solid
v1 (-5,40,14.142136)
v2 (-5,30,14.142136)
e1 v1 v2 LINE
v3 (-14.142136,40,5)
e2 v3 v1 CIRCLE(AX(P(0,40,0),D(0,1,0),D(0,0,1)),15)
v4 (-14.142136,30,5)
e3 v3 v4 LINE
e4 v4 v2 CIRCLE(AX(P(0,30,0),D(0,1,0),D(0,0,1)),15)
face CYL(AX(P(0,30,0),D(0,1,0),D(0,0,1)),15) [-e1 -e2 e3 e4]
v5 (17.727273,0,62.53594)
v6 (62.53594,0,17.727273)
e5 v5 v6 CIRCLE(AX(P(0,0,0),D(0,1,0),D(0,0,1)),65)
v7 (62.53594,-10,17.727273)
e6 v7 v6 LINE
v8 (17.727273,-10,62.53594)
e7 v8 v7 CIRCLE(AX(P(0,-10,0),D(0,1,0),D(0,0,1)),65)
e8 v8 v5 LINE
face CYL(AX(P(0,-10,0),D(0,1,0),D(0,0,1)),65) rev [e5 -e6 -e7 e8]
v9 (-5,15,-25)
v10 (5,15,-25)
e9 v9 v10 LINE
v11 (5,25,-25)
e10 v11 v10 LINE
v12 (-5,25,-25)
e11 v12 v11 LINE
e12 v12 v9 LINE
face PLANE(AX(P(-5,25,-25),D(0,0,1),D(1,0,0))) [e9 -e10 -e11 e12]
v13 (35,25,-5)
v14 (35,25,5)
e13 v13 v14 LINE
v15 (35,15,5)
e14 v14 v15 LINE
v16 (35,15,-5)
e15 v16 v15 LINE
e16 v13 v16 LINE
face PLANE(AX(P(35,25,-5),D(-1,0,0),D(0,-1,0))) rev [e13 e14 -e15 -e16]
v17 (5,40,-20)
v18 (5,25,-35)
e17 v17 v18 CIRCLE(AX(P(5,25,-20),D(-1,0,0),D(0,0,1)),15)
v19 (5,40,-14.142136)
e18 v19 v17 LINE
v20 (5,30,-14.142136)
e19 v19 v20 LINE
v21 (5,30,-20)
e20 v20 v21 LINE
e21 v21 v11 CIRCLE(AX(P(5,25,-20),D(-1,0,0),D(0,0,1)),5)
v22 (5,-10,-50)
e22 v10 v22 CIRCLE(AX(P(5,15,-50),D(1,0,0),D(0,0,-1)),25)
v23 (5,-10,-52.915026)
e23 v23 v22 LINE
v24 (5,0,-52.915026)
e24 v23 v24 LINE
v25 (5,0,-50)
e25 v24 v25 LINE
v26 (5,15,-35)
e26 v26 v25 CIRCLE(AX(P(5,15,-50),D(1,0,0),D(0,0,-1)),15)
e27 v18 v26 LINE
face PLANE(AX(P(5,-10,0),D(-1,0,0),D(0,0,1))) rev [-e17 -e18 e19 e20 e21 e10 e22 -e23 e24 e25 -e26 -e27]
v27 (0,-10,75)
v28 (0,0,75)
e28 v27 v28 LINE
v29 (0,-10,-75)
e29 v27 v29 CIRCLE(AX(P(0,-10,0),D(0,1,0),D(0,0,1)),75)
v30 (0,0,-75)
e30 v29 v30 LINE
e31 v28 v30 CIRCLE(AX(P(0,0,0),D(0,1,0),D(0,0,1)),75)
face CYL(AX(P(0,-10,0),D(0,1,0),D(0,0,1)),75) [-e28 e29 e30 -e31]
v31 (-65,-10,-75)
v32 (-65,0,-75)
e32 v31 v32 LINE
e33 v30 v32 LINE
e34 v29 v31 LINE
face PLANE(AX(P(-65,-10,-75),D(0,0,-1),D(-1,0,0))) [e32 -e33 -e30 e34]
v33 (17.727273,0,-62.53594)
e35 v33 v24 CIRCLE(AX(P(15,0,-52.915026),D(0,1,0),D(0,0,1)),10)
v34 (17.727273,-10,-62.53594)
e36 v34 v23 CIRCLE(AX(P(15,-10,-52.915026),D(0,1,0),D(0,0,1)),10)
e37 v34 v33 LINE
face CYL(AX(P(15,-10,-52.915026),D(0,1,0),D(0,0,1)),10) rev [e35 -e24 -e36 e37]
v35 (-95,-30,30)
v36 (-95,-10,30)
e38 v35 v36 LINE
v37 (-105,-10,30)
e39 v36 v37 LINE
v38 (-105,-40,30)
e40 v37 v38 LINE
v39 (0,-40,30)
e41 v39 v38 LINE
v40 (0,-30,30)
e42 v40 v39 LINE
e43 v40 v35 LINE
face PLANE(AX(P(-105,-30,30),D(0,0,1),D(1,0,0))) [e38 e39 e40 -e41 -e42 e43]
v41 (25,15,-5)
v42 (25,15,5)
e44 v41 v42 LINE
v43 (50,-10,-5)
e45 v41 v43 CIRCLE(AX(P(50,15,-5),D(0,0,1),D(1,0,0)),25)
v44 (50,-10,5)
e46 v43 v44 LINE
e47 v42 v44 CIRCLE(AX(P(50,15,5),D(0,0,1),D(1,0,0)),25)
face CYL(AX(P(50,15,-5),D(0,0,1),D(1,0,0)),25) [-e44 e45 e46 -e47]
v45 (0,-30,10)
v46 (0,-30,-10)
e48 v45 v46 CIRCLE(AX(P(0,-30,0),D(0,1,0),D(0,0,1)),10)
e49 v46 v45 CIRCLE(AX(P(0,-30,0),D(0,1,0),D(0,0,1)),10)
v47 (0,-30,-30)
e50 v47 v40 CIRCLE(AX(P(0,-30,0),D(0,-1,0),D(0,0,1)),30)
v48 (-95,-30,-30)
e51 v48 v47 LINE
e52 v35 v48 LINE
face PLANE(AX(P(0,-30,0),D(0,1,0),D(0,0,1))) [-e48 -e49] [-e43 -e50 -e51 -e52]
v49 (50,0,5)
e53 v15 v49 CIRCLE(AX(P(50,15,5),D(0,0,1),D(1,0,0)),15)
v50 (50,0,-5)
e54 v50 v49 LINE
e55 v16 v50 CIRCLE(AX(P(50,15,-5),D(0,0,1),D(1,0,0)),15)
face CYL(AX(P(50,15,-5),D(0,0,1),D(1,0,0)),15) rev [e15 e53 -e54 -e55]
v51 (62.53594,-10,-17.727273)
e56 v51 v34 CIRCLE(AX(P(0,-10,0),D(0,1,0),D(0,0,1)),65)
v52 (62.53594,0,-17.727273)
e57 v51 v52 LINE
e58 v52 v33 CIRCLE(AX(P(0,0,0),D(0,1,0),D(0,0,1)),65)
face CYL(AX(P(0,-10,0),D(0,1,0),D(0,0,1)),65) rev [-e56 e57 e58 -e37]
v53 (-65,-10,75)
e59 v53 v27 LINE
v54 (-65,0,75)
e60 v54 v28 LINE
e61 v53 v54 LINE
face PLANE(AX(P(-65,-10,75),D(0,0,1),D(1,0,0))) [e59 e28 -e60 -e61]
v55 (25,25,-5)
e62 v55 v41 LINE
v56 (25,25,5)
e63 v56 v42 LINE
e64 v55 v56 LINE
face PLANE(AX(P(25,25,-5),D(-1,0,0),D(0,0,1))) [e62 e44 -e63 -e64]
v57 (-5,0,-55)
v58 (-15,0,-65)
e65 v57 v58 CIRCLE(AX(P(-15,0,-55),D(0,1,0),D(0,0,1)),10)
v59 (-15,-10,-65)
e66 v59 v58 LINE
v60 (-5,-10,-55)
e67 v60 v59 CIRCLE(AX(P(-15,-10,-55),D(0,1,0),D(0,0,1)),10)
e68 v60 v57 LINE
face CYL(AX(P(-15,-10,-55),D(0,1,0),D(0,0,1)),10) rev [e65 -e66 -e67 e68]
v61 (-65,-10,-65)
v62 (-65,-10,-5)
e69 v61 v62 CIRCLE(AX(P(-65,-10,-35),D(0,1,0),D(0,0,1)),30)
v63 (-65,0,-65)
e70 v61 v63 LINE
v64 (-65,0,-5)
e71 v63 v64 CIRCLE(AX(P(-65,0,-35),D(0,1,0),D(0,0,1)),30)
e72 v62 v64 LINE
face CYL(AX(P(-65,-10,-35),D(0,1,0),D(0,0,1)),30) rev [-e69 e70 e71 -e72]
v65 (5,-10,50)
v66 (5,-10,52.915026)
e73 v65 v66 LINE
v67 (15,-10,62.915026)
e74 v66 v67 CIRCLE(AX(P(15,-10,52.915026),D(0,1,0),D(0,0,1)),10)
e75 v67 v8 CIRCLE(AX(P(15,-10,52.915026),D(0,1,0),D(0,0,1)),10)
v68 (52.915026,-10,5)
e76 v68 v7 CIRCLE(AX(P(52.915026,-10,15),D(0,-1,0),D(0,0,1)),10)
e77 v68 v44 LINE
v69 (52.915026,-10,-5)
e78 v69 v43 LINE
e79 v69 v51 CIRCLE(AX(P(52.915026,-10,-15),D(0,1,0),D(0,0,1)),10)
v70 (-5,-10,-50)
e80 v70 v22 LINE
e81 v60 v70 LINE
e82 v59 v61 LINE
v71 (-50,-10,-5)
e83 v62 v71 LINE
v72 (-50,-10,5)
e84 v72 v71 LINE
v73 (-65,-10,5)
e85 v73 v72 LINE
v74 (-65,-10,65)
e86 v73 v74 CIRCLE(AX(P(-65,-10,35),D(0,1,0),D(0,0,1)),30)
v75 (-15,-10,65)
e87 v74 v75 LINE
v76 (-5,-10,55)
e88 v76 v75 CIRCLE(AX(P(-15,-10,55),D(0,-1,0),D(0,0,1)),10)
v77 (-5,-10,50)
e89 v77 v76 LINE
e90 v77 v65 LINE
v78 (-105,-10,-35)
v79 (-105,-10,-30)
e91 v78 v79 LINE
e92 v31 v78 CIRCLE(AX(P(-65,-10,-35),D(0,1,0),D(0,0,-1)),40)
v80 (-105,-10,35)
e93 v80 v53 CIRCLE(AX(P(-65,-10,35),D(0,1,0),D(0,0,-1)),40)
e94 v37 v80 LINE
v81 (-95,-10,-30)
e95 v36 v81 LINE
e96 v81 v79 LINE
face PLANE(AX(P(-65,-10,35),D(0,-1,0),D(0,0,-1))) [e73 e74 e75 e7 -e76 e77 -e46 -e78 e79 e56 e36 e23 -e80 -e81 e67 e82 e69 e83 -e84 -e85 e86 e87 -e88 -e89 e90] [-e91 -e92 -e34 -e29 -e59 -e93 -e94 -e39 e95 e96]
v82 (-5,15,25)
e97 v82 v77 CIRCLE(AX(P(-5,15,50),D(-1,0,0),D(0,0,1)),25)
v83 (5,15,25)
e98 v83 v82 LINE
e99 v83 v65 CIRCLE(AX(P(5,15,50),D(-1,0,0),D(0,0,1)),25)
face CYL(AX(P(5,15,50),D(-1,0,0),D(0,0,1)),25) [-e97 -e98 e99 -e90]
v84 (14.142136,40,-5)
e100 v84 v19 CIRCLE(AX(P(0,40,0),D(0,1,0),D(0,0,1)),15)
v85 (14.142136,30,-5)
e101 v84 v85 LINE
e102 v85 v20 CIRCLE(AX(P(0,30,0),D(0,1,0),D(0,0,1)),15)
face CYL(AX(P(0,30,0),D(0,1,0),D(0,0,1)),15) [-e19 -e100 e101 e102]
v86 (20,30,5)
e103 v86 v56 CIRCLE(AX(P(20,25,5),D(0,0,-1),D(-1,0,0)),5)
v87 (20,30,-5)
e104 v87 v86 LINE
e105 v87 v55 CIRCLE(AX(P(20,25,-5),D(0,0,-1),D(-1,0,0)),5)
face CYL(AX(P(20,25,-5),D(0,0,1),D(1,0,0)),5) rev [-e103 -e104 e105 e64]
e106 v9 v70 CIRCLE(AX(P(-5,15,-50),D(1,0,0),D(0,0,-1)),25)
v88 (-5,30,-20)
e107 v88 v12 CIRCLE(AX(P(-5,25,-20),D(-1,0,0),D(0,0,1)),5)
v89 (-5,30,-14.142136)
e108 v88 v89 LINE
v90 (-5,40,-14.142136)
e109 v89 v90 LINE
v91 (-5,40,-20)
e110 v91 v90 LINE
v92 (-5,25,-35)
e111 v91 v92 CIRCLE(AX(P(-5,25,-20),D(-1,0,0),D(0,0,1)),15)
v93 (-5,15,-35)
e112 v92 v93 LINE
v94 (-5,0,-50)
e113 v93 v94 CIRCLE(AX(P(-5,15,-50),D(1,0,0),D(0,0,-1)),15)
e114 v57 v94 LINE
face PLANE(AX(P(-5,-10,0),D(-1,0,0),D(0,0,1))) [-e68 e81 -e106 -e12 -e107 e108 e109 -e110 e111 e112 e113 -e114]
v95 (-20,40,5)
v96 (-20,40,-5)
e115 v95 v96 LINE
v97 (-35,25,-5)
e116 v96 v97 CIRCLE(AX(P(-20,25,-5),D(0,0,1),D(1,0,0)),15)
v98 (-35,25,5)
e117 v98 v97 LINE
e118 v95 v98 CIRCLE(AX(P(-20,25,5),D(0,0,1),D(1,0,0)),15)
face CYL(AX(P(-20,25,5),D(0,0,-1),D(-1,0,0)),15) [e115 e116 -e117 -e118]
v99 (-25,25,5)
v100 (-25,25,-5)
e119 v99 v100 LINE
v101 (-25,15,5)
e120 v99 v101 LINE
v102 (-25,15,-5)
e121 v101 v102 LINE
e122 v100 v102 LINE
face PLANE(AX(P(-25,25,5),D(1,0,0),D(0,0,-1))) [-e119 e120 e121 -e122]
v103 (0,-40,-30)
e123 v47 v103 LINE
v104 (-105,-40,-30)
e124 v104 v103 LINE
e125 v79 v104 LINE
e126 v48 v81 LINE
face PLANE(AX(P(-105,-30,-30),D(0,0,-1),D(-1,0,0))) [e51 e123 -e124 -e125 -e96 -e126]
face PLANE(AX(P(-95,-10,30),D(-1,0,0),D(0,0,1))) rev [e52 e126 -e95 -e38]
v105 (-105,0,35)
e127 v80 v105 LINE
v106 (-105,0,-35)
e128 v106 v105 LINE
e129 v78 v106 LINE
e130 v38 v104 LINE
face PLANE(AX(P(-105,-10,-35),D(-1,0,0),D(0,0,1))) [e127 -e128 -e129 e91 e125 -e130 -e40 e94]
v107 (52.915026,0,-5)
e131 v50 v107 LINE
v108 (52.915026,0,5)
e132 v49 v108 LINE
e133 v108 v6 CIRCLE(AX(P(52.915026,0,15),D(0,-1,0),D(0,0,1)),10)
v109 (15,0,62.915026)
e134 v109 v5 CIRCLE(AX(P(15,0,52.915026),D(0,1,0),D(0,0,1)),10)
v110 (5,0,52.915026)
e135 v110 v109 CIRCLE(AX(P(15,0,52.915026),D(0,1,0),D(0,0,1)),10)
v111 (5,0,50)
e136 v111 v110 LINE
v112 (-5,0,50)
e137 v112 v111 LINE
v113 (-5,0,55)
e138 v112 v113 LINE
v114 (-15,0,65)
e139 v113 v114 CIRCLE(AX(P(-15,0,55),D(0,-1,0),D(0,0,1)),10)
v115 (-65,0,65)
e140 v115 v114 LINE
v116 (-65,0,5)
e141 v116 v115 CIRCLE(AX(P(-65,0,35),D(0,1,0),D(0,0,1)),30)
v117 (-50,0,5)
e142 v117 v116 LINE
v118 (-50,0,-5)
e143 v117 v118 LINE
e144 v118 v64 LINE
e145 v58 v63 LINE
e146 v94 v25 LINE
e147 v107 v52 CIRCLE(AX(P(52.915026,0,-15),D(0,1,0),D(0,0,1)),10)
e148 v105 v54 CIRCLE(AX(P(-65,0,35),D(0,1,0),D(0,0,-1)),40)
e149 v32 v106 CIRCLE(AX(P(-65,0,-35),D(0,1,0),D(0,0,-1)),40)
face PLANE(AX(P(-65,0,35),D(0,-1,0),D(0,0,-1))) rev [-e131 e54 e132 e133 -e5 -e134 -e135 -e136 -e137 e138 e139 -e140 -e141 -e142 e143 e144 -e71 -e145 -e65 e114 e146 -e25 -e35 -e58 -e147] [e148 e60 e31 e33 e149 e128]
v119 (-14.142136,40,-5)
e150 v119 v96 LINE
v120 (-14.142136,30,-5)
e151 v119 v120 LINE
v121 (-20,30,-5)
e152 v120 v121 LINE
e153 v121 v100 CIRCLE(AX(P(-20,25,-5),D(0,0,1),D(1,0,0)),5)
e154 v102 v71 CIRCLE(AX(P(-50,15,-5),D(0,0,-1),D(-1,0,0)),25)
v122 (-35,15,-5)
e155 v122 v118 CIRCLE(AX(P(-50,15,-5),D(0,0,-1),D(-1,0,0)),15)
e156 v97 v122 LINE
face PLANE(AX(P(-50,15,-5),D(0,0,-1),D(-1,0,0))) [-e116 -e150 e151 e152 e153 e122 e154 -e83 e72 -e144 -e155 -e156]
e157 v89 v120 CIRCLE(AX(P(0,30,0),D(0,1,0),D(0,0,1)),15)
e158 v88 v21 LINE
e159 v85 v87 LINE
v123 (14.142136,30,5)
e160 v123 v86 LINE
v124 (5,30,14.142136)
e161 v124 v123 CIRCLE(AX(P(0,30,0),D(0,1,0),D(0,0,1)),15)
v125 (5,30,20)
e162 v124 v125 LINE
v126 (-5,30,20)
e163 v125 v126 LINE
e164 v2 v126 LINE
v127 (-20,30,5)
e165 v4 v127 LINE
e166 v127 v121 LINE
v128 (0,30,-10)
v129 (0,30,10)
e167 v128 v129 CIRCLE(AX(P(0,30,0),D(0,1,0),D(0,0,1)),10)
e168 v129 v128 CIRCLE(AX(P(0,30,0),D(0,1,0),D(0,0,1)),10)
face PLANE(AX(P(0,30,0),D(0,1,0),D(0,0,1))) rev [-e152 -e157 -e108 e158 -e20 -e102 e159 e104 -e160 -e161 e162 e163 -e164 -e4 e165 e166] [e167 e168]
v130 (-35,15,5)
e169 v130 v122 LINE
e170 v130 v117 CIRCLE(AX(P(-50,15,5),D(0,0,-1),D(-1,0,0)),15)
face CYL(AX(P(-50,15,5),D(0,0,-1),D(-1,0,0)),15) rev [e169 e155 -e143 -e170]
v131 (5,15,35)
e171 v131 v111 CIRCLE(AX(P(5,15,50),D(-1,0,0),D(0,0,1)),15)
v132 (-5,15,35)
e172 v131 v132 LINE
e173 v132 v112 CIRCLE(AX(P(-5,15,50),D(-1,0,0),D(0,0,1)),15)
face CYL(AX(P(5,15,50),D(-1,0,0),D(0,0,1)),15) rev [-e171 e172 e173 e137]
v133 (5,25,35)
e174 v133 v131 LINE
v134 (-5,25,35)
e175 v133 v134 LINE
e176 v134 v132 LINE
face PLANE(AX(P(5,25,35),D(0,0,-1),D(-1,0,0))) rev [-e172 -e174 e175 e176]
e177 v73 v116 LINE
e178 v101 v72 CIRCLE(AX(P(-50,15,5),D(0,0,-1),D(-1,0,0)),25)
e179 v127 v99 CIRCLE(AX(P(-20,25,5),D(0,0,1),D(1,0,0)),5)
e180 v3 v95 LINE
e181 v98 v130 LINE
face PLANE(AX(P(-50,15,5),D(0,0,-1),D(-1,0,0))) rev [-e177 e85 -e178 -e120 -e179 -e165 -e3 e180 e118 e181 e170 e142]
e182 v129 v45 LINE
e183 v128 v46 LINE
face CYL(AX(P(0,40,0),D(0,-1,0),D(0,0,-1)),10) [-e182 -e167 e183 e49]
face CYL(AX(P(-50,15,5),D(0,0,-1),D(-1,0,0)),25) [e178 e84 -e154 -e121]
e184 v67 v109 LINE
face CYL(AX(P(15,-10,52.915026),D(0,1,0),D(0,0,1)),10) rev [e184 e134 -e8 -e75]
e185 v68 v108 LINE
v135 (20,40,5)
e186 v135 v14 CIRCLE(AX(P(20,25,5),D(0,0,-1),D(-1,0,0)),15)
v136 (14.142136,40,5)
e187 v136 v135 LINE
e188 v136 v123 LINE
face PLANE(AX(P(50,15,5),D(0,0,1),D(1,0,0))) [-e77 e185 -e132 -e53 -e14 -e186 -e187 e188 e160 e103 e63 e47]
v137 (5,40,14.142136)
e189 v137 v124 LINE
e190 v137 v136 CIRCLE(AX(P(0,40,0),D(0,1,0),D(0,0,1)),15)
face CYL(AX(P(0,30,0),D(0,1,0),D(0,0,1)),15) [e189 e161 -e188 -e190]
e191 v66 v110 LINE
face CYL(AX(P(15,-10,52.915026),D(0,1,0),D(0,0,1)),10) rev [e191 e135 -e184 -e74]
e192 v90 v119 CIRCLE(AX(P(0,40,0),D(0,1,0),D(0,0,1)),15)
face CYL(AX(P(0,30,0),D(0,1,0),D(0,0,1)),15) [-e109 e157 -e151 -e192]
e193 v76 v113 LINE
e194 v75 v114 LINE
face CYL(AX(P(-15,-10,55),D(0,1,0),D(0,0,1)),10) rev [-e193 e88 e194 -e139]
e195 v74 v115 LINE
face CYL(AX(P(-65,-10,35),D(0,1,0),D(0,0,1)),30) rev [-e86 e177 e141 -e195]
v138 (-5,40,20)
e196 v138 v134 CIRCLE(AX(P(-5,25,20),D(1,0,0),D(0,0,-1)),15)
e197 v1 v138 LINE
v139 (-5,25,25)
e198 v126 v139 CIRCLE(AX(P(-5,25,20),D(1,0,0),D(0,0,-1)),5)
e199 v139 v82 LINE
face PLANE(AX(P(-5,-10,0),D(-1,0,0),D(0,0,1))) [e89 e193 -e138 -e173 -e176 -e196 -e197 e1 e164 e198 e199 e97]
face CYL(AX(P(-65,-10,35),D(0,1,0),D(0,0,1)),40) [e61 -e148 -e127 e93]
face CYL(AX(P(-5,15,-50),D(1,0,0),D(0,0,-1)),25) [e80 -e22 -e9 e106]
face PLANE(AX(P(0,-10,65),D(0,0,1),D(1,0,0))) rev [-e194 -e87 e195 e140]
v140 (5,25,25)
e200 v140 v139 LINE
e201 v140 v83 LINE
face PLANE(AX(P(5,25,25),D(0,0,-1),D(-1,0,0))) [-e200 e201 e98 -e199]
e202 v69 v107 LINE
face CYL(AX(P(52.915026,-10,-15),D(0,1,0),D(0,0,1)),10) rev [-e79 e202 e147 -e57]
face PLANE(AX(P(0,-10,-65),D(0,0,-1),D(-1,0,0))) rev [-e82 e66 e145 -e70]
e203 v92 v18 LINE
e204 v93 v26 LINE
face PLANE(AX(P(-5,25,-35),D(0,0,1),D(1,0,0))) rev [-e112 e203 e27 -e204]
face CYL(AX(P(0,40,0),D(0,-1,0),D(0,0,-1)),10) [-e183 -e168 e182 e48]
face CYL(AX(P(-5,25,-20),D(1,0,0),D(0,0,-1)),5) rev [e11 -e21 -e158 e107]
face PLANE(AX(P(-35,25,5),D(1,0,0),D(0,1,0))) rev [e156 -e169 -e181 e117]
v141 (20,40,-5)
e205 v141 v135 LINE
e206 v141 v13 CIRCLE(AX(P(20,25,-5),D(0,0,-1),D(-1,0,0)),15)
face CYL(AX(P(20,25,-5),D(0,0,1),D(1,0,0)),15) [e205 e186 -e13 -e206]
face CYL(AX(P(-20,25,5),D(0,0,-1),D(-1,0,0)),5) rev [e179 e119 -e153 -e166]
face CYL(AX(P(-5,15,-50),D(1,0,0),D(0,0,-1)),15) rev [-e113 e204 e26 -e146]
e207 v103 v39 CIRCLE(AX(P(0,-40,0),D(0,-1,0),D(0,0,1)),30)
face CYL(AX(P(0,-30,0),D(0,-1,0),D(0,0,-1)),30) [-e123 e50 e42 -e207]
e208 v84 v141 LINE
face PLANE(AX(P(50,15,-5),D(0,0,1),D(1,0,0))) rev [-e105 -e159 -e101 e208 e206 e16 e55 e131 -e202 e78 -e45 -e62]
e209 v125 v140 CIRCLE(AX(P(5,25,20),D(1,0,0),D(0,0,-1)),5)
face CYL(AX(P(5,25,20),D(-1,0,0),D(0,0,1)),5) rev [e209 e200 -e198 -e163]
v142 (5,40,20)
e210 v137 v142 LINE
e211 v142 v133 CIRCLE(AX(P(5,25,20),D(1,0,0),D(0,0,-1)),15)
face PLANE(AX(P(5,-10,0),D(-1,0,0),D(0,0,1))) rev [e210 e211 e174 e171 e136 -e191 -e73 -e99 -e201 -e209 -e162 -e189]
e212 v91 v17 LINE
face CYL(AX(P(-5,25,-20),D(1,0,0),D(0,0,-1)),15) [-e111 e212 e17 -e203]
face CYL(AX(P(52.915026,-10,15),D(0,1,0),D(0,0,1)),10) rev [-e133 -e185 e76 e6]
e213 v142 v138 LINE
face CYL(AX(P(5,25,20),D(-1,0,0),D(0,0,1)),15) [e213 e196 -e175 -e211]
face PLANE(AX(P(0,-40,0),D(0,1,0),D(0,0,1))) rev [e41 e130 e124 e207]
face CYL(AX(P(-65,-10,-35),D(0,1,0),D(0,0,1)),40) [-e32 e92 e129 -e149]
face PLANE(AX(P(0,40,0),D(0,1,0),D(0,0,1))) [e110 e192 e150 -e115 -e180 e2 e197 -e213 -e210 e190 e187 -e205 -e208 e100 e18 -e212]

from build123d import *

# Parameters (mm, degrees)
CENTRAL_POST_SKETCH_R       = 10
CENTRAL_POST_20_DEPTH       = 40
MOUNTING_PLATE_DEPTH        = 10
RECTANGULAR_PAD_60X30_DEPTH = 10
SIDE_WALL_SKETCH_W          = 10
SIDE_WALL_SKETCH_H          = 20
SIDE_WALL_DEPTH             = 30
HUB_SKETCH_R                = 15
HUB_30_DEPTH                = 10
PLATE_CUTOUTS_SKETCH_R      = 10
PLATE_CUTOUTS_DEPTH         = 10
SUPPORT_RIB_DEPTH           = 5
RIB_PATTERN_4X_COUNT        = 4


with BuildPart() as part:
    # Central Post Sketch → Central Post Ø20 (new, symmetric)
    with BuildSketch(Plane(origin=(0, 0, 0), x_dir=(1, 0, 0), z_dir=(0, 1, 0))):
        with Locations(Location((0, 0, 0), (0, 0, 270))):
            Circle(CENTRAL_POST_SKETCH_R)
    extrude(amount=CENTRAL_POST_20_DEPTH, both=True)

    # Plate Outline Sketch → Mounting Plate (add)
    with BuildSketch(Plane(origin=(0, 0, 0), x_dir=(1, 0, 0), z_dir=(0, 1, 0))):
        with BuildLine():
            Line((-65, 75), (0, 75))
            ThreePointArc((0, 75), (75, 0), (0, -75))
            Line((0, -75), (-65, -75))
            ThreePointArc((-65, -75), (-93.284271247, -63.284271247), (-105, -35))
            Line((-105, -35), (-105, 35))
            ThreePointArc((-105, 35), (-93.284271247, 63.284271247), (-65, 75))
        make_face()
    extrude(amount=-MOUNTING_PLATE_DEPTH)

    # Pad Sketch → Rectangular Pad 60x30 (add)
    with BuildSketch(Plane.XZ.offset(40)):
        with BuildLine():
            Line((-105, 30), (0, 30))
            ThreePointArc((0, 30), (30, 0), (0, -30))
            Line((0, -30), (-105, -30))
            Line((-105, -30), (-105, 30))
        make_face()
    extrude(amount=-RECTANGULAR_PAD_60X30_DEPTH)

    # Side Wall Sketch → Side Wall (add, symmetric)
    with BuildSketch(Plane.XY):
        with Locations((-100, -20)):
            Rectangle(SIDE_WALL_SKETCH_W, SIDE_WALL_SKETCH_H)
    extrude(amount=SIDE_WALL_DEPTH, both=True)

    # Hub Sketch → Hub Ø30 (add)
    with BuildSketch(Plane(origin=(0, 40, 0), x_dir=(1, 0, 0), z_dir=(0, 1, 0))):
        with Locations(Location((0, 0, 0), (0, 0, 270))):
            Circle(HUB_SKETCH_R)
    extrude(amount=-HUB_30_DEPTH)

    # Plate Cutouts Sketch → Plate Cutouts (cut)
    with BuildSketch(Plane(origin=(0, 0, 0), x_dir=(1, 0, 0), z_dir=(0, 1, 0))):
        with BuildLine():
            ThreePointArc((62.53594008, 17.727272727), (45.961940777, 45.961940777), (17.727272727, 62.53594008))
            ThreePointArc((17.727272727, 62.53594008), (8.969773108, 60.892266573), (5, 52.915026221))
            Line((5, 52.915026221), (5, 50))
            Line((5, 50), (-5, 50))
            Line((-5, 50), (-5, 55))
            ThreePointArc((-5, 55), (-7.928932188, 62.071067812), (-15, 65))
            Line((-15, 65), (-65, 65))
            ThreePointArc((-65, 65), (-95, 35), (-65, 5))
            Line((-65, 5), (-65, -5))
            ThreePointArc((-65, -5), (-95, -35), (-65, -65))
            Line((-65, -65), (-15, -65))
            ThreePointArc((-15, -65), (-7.928932188, -62.071067812), (-5, -55))
            Line((-5, -55), (-5, -50))
            Line((-5, -50), (5, -50))
            Line((5, -50), (5, -52.915026221))
            ThreePointArc((5, -52.915026221), (8.969773108, -60.892266573), (17.727272727, -62.53594008))
            ThreePointArc((17.727272727, -62.53594008), (45.961940777, -45.961940777), (62.53594008, -17.727272727))
            ThreePointArc((62.53594008, -17.727272727), (60.892266573, -8.969773108), (52.915026221, -5))
            Line((52.915026221, -5), (52.915026221, 5))
            ThreePointArc((52.915026221, 5), (60.892266573, 8.969773108), (62.53594008, 17.727272727))
        make_face()
        with Locations(Location((0, 0, 0), (0, 0, 270))):
            Circle(PLATE_CUTOUTS_SKETCH_R, mode=Mode.SUBTRACT)
    extrude(amount=-PLATE_CUTOUTS_DEPTH, mode=Mode.SUBTRACT)

    # Support Rib Sketch → Support Rib (add, symmetric)
    with BuildSketch(Plane.XY):
        with BuildLine():
            Line((0, 40), (-20, 40))
            ThreePointArc((-20, 40), (-30.606601718, 35.606601718), (-35, 25))
            Line((-35, 25), (-35, 15))
            ThreePointArc((-35, 15), (-39.393398282, 4.393398282), (-50, 0))
            Line((-50, 0), (-65, 0))
            Line((-65, 0), (-65, -10))
            Line((-65, -10), (-50, -10))
            ThreePointArc((-50, -10), (-32.32233047, -2.67766953), (-25, 15))
            Line((-25, 15), (-25, 25))
            ThreePointArc((-25, 25), (-23.535533906, 28.535533906), (-20, 30))
            Line((-20, 30), (0, 30))
            Line((0, 30), (0, 40))
        make_face()
    support_rib = extrude(amount=SUPPORT_RIB_DEPTH, both=True)

    # Rib Pattern 4x: Support Rib ×4 about axis
    rib_pattern_4x_axis = Axis((0, 0, 0), (0, 1, 0))
    for i in range(1, RIB_PATTERN_4X_COUNT):
        add(support_rib.rotate(rib_pattern_4x_axis, i * 360 / RIB_PATTERN_4X_COUNT))


solid = part.part
